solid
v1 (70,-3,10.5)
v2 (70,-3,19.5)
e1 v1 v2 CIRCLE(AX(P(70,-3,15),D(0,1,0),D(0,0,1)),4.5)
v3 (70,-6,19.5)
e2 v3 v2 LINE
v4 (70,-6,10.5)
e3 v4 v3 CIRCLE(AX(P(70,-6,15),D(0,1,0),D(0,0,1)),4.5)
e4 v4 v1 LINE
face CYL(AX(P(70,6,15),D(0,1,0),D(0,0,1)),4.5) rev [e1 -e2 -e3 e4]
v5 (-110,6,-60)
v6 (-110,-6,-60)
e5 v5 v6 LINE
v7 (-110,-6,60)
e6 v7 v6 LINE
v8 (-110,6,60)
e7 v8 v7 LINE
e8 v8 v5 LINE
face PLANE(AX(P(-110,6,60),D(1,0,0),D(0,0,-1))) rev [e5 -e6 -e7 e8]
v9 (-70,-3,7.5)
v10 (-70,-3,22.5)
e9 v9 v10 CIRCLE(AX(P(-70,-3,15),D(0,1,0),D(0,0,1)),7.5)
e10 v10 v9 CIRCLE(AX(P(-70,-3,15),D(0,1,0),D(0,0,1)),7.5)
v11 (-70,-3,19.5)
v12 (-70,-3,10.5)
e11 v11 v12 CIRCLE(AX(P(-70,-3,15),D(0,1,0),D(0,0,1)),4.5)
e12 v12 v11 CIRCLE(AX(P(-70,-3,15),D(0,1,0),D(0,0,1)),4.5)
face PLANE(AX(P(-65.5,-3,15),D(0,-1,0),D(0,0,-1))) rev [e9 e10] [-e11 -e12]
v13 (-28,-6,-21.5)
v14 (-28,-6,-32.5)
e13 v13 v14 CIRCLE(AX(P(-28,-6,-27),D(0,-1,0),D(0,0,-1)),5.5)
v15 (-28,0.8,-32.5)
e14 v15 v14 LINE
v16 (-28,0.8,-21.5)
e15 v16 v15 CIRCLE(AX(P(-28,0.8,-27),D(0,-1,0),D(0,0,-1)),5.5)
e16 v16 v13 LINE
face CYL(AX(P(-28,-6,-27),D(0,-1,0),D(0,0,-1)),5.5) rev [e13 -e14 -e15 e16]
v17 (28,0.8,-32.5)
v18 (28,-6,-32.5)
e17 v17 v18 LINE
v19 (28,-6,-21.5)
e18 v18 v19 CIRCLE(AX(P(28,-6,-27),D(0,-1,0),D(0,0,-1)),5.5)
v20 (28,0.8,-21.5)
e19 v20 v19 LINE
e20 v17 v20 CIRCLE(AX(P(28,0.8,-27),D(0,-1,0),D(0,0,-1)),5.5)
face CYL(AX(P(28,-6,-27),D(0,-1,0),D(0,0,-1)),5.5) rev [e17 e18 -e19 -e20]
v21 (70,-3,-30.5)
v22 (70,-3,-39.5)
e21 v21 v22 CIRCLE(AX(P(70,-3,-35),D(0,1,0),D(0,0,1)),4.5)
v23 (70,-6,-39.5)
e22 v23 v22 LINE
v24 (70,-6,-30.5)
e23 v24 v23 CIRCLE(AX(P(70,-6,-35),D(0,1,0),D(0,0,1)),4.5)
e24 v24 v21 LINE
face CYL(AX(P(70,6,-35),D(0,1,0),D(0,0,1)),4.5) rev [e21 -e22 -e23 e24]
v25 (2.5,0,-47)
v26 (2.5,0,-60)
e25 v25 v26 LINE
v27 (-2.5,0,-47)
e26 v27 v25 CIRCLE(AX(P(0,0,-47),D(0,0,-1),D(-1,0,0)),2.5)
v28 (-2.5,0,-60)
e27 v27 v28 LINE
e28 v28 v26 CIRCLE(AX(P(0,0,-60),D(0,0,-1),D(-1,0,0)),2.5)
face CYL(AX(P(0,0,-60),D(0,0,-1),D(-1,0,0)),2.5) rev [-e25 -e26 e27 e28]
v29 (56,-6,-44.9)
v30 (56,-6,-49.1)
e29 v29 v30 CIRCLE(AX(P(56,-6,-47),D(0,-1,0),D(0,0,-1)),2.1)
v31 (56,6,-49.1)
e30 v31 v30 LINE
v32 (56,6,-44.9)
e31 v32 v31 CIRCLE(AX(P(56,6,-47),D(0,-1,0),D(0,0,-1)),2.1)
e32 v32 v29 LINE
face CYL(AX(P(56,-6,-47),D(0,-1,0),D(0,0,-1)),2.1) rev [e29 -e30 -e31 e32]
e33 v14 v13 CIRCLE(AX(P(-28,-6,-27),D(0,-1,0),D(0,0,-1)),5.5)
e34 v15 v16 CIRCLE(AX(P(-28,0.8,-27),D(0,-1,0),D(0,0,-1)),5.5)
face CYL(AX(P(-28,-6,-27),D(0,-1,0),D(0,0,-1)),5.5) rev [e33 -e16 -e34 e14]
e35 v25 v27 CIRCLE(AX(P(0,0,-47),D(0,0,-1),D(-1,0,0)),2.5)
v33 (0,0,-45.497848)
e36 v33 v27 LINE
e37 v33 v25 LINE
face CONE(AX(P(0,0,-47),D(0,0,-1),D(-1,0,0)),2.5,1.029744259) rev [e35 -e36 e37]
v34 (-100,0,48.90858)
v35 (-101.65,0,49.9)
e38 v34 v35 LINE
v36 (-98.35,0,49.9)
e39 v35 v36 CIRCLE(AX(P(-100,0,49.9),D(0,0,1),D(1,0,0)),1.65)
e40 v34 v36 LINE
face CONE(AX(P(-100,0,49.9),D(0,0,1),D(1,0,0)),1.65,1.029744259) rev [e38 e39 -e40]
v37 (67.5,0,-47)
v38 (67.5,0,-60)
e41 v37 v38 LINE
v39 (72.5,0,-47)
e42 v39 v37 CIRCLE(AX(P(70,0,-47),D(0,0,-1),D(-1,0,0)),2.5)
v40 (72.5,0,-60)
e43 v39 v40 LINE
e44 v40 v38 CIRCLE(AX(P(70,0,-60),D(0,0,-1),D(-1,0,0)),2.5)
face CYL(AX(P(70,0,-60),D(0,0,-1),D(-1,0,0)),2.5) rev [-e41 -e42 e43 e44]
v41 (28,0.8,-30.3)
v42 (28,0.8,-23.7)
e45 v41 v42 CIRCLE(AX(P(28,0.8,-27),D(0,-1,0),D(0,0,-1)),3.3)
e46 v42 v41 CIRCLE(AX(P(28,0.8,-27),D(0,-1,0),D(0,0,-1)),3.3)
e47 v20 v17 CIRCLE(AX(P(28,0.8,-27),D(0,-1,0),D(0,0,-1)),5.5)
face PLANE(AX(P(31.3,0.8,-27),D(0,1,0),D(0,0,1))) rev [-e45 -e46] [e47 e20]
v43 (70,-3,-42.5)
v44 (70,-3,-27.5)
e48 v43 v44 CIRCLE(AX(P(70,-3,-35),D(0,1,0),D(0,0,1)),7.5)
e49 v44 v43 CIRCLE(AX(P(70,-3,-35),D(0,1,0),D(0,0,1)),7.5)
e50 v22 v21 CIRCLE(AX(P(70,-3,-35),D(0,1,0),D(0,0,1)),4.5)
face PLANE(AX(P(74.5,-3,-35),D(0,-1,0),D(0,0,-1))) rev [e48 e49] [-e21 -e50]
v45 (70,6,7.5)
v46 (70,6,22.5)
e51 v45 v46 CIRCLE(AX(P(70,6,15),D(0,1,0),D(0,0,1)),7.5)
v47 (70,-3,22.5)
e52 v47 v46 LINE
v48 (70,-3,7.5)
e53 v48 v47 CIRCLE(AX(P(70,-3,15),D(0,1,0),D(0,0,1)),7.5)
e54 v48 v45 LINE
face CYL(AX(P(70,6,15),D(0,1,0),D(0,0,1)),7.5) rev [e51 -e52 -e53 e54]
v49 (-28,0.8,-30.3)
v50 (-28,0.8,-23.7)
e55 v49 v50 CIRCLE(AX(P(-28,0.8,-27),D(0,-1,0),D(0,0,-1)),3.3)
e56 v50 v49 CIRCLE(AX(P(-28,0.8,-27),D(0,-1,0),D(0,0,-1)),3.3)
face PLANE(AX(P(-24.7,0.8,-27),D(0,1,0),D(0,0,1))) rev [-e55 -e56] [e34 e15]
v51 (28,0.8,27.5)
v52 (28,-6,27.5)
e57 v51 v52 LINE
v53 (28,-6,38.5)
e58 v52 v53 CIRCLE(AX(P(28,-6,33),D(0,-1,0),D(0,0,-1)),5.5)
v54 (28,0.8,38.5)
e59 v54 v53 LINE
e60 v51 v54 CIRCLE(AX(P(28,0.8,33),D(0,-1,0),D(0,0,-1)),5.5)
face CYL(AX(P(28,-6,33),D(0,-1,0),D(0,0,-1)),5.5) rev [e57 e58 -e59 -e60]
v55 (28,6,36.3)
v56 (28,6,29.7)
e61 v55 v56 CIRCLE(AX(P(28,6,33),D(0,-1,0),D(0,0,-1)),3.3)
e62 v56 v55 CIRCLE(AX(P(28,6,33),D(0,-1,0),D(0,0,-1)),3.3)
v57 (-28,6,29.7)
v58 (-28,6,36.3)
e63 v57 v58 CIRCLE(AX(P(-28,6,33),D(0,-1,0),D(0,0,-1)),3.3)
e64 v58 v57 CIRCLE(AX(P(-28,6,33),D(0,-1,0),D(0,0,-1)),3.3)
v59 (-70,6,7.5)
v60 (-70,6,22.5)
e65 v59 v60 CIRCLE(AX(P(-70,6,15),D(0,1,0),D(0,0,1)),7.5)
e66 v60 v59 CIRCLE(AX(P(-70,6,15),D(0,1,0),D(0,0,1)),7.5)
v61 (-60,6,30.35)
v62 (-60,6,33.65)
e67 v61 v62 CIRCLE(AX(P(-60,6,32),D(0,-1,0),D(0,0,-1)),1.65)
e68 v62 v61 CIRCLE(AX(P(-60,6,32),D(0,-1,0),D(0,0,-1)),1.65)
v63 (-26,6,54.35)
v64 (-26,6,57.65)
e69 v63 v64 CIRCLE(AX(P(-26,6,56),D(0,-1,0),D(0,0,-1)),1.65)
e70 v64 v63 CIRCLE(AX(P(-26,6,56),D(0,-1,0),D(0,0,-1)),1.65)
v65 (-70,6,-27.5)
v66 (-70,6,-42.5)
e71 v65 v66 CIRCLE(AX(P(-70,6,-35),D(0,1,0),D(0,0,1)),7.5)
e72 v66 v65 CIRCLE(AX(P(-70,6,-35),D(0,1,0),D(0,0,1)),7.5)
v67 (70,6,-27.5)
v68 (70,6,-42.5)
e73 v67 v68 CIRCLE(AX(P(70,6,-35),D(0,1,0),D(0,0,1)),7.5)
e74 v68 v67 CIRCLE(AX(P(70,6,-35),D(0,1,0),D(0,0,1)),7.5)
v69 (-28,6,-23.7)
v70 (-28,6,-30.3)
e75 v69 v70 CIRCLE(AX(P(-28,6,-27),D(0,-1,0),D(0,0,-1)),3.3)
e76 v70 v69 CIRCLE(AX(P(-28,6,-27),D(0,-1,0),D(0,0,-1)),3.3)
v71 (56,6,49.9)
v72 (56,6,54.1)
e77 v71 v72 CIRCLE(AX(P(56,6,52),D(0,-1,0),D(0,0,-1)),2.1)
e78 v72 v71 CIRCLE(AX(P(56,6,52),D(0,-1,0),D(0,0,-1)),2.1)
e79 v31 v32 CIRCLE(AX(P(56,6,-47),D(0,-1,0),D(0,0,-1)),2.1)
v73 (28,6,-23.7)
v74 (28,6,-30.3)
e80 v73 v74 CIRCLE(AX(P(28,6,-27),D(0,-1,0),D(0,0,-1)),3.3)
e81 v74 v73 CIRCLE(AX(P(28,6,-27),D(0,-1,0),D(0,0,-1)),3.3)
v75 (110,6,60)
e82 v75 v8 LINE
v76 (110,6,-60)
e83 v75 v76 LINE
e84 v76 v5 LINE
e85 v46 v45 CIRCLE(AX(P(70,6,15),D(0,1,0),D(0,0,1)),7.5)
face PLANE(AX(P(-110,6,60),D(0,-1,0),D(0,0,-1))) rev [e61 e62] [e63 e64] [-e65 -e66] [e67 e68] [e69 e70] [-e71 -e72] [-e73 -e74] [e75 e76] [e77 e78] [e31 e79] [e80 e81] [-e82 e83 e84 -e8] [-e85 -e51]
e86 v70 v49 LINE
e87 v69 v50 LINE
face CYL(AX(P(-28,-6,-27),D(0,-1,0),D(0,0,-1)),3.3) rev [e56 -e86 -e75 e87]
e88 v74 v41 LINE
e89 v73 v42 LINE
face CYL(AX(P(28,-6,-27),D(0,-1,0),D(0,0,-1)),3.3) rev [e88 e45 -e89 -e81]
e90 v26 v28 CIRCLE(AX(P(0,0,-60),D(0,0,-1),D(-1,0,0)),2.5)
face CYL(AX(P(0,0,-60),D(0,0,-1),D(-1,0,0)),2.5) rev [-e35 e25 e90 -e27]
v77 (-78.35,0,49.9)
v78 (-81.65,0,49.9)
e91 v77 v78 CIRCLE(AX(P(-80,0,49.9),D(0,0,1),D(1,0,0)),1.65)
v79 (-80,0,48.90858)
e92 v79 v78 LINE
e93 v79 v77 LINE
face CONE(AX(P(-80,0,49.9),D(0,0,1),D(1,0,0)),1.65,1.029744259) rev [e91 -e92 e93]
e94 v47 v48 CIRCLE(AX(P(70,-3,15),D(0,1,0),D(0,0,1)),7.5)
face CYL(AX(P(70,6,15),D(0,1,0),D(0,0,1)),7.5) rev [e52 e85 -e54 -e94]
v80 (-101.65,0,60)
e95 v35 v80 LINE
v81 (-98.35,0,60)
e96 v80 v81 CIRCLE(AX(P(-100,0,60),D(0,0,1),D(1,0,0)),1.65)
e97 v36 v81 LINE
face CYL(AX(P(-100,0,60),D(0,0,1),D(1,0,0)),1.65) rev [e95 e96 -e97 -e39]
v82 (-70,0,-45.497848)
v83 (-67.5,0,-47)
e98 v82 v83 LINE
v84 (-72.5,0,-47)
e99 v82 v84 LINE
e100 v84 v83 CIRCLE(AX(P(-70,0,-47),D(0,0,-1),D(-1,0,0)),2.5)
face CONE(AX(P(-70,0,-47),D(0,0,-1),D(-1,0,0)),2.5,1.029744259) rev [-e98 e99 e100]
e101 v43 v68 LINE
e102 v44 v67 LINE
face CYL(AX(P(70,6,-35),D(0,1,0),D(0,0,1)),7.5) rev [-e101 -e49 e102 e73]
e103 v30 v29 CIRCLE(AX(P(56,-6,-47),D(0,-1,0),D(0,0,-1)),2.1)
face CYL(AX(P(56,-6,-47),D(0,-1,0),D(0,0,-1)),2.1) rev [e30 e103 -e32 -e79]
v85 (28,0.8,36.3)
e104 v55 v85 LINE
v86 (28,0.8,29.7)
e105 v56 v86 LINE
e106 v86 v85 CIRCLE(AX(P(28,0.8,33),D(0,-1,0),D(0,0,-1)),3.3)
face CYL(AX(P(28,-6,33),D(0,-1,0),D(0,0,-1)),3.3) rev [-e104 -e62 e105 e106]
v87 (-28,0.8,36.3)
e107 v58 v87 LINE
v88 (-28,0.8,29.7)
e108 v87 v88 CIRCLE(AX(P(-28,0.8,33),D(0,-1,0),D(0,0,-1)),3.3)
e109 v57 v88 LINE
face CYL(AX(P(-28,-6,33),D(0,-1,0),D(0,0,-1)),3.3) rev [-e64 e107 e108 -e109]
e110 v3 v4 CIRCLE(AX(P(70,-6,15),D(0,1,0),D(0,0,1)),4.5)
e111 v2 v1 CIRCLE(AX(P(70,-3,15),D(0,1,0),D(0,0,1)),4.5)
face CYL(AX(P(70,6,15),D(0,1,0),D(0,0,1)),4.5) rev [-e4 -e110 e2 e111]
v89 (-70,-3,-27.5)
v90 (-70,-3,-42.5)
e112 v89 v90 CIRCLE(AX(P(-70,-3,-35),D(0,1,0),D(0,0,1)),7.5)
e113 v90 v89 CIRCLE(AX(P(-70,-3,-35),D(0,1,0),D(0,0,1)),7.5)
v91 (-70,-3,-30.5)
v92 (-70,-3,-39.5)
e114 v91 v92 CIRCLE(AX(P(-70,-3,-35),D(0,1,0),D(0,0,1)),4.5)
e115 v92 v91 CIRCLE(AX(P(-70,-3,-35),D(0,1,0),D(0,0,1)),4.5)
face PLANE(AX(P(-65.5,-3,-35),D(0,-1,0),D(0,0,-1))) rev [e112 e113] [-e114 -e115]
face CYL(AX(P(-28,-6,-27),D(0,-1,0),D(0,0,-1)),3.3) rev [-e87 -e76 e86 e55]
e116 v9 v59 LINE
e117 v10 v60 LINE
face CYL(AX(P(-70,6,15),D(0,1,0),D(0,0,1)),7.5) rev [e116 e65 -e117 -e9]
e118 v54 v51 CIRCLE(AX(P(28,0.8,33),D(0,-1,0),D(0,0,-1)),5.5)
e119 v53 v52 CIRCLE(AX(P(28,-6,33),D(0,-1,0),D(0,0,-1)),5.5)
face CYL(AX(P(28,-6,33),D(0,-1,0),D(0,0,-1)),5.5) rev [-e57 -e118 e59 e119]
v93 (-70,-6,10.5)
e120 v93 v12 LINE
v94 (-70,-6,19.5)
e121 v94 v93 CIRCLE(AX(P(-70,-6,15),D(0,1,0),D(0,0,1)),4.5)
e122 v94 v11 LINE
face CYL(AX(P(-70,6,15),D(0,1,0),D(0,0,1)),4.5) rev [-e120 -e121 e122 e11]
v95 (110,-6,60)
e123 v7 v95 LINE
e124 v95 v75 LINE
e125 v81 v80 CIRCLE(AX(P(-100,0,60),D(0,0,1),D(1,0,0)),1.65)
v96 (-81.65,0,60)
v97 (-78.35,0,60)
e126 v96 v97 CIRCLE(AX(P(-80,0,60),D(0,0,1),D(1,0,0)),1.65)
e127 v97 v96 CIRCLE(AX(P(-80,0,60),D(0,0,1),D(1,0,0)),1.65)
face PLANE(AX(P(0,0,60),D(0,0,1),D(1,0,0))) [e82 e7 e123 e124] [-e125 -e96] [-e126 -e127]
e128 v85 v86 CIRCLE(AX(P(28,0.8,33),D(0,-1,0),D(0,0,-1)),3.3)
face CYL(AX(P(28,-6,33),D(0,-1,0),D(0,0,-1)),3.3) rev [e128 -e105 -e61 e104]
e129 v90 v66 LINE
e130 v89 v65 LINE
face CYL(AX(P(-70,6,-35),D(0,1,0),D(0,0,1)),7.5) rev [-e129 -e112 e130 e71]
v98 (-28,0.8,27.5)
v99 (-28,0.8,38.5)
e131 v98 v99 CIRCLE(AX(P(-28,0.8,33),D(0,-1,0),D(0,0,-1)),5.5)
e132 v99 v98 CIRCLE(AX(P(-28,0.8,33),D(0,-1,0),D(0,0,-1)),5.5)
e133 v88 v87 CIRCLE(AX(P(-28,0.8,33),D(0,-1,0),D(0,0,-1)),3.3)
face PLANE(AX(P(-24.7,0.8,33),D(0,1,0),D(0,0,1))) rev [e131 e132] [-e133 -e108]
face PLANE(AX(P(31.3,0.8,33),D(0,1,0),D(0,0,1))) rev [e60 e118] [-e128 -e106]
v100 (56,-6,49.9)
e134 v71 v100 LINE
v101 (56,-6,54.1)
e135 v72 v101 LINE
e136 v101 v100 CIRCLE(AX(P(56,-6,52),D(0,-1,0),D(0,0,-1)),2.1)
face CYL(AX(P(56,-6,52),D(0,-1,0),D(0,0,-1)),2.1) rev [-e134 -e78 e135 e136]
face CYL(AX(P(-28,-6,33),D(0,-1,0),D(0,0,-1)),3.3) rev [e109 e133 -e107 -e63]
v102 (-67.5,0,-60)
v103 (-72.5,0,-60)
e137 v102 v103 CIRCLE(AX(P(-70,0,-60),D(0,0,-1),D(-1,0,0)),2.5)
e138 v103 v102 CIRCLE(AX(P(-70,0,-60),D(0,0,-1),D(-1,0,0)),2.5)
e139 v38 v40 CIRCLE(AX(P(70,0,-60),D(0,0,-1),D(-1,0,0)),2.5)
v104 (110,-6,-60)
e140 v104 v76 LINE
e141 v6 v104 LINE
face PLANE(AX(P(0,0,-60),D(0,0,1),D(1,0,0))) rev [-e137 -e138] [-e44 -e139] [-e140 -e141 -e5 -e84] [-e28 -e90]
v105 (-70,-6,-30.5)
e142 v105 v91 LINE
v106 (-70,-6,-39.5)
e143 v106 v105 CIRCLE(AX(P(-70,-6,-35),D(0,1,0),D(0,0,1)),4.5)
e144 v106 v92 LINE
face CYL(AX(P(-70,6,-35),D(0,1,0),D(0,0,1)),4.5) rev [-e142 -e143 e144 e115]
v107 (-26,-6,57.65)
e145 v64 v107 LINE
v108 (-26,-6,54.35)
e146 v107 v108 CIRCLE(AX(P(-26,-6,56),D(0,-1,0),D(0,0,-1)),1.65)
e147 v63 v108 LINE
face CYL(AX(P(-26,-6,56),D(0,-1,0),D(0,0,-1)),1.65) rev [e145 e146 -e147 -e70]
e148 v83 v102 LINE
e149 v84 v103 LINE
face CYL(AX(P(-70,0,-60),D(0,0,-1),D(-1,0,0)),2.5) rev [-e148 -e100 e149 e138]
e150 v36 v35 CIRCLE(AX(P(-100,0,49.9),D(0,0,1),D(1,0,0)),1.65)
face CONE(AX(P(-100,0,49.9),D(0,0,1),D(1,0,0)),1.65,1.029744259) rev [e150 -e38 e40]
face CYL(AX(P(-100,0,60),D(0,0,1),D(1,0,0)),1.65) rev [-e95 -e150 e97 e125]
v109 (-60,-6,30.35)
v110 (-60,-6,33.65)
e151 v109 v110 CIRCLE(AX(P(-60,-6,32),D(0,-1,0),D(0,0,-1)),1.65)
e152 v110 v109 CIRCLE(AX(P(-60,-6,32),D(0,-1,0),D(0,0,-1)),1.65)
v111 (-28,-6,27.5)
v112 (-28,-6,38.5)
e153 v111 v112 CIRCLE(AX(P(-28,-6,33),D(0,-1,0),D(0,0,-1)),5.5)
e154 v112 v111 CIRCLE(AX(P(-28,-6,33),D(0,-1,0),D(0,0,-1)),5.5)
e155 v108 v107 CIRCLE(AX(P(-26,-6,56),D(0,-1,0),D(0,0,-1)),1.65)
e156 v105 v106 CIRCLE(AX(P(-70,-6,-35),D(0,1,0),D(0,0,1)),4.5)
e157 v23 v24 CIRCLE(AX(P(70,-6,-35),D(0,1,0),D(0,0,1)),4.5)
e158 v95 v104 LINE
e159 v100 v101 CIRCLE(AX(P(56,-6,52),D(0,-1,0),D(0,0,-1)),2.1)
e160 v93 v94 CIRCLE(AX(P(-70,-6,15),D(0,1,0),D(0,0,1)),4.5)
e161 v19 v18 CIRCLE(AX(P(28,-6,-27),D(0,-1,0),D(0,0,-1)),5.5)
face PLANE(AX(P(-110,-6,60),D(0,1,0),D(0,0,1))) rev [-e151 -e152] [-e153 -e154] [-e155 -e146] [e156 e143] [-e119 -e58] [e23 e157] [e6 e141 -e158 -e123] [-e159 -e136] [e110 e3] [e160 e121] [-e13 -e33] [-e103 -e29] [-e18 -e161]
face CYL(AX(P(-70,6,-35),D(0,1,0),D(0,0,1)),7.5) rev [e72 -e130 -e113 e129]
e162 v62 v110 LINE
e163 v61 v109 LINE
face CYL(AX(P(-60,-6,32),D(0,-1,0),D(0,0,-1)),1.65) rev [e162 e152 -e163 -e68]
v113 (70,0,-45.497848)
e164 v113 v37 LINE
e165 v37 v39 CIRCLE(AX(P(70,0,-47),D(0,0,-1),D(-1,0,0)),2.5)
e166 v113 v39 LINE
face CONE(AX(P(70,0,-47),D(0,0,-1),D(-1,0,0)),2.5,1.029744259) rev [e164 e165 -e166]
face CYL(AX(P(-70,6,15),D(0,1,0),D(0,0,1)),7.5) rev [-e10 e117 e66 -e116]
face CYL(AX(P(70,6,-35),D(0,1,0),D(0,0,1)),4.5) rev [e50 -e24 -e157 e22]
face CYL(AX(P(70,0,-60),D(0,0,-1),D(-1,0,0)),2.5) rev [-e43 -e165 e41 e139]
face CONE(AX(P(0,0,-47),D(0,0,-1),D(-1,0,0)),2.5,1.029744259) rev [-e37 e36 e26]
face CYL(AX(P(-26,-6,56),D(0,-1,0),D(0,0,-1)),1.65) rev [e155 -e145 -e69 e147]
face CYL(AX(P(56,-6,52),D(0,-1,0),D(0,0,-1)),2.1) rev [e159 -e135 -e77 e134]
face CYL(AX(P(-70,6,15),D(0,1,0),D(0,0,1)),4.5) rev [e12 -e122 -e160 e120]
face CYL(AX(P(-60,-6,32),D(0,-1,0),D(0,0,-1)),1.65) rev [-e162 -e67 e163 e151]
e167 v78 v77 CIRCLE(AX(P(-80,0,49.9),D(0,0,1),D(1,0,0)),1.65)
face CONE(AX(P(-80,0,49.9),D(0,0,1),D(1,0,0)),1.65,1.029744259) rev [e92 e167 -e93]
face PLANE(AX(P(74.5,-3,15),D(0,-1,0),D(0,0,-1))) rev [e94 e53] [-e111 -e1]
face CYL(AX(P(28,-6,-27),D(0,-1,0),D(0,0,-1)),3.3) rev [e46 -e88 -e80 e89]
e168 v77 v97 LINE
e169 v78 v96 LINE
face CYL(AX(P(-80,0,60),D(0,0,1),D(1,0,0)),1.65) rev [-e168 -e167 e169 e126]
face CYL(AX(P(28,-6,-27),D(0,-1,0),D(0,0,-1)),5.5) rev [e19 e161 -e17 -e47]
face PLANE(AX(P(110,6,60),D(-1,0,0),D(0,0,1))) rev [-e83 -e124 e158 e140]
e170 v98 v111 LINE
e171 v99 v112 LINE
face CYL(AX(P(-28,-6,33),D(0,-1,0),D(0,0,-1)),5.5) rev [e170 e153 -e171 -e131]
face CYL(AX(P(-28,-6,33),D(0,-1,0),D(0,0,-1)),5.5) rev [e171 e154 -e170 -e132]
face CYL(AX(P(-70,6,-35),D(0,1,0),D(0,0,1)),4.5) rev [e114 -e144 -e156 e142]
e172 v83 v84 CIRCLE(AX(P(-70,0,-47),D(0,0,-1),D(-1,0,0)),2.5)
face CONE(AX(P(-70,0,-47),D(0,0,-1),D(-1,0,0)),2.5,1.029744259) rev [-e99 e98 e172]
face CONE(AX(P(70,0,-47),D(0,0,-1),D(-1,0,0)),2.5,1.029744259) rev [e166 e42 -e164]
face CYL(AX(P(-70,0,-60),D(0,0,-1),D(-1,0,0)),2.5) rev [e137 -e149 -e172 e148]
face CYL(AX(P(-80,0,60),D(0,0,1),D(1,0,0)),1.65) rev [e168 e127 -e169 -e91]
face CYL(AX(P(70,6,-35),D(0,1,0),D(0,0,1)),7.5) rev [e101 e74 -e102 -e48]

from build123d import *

# Parameters (mm, degrees)
SKETCH_1_W                  = 220
SKETCH_1_H                  = 12
EXTRUDE_1_DEPTH             = 60
HOLE_WIZARD_M6_1_D          = 5
HOLE_WIZARD_M6_1_DEPTH      = 13
HOLE_WIZARD_M6_1_TIP        = 1.502151548
HOLE_WIZARD_2_D             = 9
HOLE_WIZARD_2_CBORE_D       = 15
HOLE_WIZARD_2_CBORE_DEPTH   = 9
HOLE_WIZARD_2_2_D           = 6.6
HOLE_WIZARD_2_2_CBORE_D     = 11
HOLE_WIZARD_2_2_CBORE_DEPTH = 6.8
HOLE_WIZARD_M4_1_D          = 3.3
HOLE_WIZARD_M5_2_D          = 4.2
HOLE_WIZARD_M4_2_D          = 3.3
HOLE_WIZARD_M4_2_DEPTH      = 10.1
HOLE_WIZARD_M4_2_TIP        = 0.991420021


with BuildPart() as part:
    # 草图1 → 凸台-拉伸1 (new, symmetric)
    with BuildSketch(Plane.XY):
        Rectangle(SKETCH_1_W, SKETCH_1_H)
    extrude(amount=EXTRUDE_1_DEPTH, both=True)

    # M6 螺纹孔1
    with Locations(Plane(origin=(70, 0, -60), x_dir=(-1, 0, 0), z_dir=(0, 0, -1))):
        with Locations((0, 0), (70, 0), (140, 0)):
            Hole(HOLE_WIZARD_M6_1_D / 2, depth=HOLE_WIZARD_M6_1_DEPTH)
            with Locations((0, 0, -(HOLE_WIZARD_M6_1_DEPTH + HOLE_WIZARD_M6_1_TIP / 2))):  # 118° drill point
                Cone(0, HOLE_WIZARD_M6_1_D / 2, HOLE_WIZARD_M6_1_TIP, mode=Mode.SUBTRACT)

    # Hole Wizard 2 (through all)
    with Locations(Plane(origin=(-70, 6, -35), x_dir=(0, 0, 1), z_dir=(0, 1, 0))):
        with Locations((0, 0), (50, 0), (0, 140), (50, 140)):
            CounterBoreHole(HOLE_WIZARD_2_D / 2, HOLE_WIZARD_2_CBORE_D / 2, HOLE_WIZARD_2_CBORE_DEPTH)

    # Hole Wizard 2 2 (through all)
    with Locations(Plane(origin=(-28, -6, -27), x_dir=(0, 0, -1), z_dir=(0, -1, 0))):
        with Locations((0, 0), (0, 56), (-60, 56), (-60, 0)):
            CounterBoreHole(HOLE_WIZARD_2_2_D / 2, HOLE_WIZARD_2_2_CBORE_D / 2, HOLE_WIZARD_2_2_CBORE_DEPTH)

    # M4 螺纹孔1 (through all)
    with Locations(Plane(origin=(0, -6, 0), x_dir=(-1, 0, 0), z_dir=(0, -1, 0))):
        with Locations((26, -56), (60, -32)):
            Hole(HOLE_WIZARD_M4_1_D / 2)

    # M5 螺纹孔2 (through all)
    with Locations(Plane(origin=(0, -6, 0), x_dir=(-1, 0, 0), z_dir=(0, -1, 0))):
        with Locations((-56, -52), (-56, 47)):
            Hole(HOLE_WIZARD_M5_2_D / 2)

    # M4 螺纹孔2
    with Locations(Plane.XY.offset(60)):
        with Locations((-100, 0), (-80, 0)):
            Hole(HOLE_WIZARD_M4_2_D / 2, depth=HOLE_WIZARD_M4_2_DEPTH)
            with Locations((0, 0, -(HOLE_WIZARD_M4_2_DEPTH + HOLE_WIZARD_M4_2_TIP / 2))):  # 118° drill point
                Cone(0, HOLE_WIZARD_M4_2_D / 2, HOLE_WIZARD_M4_2_TIP, mode=Mode.SUBTRACT)


solid = part.part
